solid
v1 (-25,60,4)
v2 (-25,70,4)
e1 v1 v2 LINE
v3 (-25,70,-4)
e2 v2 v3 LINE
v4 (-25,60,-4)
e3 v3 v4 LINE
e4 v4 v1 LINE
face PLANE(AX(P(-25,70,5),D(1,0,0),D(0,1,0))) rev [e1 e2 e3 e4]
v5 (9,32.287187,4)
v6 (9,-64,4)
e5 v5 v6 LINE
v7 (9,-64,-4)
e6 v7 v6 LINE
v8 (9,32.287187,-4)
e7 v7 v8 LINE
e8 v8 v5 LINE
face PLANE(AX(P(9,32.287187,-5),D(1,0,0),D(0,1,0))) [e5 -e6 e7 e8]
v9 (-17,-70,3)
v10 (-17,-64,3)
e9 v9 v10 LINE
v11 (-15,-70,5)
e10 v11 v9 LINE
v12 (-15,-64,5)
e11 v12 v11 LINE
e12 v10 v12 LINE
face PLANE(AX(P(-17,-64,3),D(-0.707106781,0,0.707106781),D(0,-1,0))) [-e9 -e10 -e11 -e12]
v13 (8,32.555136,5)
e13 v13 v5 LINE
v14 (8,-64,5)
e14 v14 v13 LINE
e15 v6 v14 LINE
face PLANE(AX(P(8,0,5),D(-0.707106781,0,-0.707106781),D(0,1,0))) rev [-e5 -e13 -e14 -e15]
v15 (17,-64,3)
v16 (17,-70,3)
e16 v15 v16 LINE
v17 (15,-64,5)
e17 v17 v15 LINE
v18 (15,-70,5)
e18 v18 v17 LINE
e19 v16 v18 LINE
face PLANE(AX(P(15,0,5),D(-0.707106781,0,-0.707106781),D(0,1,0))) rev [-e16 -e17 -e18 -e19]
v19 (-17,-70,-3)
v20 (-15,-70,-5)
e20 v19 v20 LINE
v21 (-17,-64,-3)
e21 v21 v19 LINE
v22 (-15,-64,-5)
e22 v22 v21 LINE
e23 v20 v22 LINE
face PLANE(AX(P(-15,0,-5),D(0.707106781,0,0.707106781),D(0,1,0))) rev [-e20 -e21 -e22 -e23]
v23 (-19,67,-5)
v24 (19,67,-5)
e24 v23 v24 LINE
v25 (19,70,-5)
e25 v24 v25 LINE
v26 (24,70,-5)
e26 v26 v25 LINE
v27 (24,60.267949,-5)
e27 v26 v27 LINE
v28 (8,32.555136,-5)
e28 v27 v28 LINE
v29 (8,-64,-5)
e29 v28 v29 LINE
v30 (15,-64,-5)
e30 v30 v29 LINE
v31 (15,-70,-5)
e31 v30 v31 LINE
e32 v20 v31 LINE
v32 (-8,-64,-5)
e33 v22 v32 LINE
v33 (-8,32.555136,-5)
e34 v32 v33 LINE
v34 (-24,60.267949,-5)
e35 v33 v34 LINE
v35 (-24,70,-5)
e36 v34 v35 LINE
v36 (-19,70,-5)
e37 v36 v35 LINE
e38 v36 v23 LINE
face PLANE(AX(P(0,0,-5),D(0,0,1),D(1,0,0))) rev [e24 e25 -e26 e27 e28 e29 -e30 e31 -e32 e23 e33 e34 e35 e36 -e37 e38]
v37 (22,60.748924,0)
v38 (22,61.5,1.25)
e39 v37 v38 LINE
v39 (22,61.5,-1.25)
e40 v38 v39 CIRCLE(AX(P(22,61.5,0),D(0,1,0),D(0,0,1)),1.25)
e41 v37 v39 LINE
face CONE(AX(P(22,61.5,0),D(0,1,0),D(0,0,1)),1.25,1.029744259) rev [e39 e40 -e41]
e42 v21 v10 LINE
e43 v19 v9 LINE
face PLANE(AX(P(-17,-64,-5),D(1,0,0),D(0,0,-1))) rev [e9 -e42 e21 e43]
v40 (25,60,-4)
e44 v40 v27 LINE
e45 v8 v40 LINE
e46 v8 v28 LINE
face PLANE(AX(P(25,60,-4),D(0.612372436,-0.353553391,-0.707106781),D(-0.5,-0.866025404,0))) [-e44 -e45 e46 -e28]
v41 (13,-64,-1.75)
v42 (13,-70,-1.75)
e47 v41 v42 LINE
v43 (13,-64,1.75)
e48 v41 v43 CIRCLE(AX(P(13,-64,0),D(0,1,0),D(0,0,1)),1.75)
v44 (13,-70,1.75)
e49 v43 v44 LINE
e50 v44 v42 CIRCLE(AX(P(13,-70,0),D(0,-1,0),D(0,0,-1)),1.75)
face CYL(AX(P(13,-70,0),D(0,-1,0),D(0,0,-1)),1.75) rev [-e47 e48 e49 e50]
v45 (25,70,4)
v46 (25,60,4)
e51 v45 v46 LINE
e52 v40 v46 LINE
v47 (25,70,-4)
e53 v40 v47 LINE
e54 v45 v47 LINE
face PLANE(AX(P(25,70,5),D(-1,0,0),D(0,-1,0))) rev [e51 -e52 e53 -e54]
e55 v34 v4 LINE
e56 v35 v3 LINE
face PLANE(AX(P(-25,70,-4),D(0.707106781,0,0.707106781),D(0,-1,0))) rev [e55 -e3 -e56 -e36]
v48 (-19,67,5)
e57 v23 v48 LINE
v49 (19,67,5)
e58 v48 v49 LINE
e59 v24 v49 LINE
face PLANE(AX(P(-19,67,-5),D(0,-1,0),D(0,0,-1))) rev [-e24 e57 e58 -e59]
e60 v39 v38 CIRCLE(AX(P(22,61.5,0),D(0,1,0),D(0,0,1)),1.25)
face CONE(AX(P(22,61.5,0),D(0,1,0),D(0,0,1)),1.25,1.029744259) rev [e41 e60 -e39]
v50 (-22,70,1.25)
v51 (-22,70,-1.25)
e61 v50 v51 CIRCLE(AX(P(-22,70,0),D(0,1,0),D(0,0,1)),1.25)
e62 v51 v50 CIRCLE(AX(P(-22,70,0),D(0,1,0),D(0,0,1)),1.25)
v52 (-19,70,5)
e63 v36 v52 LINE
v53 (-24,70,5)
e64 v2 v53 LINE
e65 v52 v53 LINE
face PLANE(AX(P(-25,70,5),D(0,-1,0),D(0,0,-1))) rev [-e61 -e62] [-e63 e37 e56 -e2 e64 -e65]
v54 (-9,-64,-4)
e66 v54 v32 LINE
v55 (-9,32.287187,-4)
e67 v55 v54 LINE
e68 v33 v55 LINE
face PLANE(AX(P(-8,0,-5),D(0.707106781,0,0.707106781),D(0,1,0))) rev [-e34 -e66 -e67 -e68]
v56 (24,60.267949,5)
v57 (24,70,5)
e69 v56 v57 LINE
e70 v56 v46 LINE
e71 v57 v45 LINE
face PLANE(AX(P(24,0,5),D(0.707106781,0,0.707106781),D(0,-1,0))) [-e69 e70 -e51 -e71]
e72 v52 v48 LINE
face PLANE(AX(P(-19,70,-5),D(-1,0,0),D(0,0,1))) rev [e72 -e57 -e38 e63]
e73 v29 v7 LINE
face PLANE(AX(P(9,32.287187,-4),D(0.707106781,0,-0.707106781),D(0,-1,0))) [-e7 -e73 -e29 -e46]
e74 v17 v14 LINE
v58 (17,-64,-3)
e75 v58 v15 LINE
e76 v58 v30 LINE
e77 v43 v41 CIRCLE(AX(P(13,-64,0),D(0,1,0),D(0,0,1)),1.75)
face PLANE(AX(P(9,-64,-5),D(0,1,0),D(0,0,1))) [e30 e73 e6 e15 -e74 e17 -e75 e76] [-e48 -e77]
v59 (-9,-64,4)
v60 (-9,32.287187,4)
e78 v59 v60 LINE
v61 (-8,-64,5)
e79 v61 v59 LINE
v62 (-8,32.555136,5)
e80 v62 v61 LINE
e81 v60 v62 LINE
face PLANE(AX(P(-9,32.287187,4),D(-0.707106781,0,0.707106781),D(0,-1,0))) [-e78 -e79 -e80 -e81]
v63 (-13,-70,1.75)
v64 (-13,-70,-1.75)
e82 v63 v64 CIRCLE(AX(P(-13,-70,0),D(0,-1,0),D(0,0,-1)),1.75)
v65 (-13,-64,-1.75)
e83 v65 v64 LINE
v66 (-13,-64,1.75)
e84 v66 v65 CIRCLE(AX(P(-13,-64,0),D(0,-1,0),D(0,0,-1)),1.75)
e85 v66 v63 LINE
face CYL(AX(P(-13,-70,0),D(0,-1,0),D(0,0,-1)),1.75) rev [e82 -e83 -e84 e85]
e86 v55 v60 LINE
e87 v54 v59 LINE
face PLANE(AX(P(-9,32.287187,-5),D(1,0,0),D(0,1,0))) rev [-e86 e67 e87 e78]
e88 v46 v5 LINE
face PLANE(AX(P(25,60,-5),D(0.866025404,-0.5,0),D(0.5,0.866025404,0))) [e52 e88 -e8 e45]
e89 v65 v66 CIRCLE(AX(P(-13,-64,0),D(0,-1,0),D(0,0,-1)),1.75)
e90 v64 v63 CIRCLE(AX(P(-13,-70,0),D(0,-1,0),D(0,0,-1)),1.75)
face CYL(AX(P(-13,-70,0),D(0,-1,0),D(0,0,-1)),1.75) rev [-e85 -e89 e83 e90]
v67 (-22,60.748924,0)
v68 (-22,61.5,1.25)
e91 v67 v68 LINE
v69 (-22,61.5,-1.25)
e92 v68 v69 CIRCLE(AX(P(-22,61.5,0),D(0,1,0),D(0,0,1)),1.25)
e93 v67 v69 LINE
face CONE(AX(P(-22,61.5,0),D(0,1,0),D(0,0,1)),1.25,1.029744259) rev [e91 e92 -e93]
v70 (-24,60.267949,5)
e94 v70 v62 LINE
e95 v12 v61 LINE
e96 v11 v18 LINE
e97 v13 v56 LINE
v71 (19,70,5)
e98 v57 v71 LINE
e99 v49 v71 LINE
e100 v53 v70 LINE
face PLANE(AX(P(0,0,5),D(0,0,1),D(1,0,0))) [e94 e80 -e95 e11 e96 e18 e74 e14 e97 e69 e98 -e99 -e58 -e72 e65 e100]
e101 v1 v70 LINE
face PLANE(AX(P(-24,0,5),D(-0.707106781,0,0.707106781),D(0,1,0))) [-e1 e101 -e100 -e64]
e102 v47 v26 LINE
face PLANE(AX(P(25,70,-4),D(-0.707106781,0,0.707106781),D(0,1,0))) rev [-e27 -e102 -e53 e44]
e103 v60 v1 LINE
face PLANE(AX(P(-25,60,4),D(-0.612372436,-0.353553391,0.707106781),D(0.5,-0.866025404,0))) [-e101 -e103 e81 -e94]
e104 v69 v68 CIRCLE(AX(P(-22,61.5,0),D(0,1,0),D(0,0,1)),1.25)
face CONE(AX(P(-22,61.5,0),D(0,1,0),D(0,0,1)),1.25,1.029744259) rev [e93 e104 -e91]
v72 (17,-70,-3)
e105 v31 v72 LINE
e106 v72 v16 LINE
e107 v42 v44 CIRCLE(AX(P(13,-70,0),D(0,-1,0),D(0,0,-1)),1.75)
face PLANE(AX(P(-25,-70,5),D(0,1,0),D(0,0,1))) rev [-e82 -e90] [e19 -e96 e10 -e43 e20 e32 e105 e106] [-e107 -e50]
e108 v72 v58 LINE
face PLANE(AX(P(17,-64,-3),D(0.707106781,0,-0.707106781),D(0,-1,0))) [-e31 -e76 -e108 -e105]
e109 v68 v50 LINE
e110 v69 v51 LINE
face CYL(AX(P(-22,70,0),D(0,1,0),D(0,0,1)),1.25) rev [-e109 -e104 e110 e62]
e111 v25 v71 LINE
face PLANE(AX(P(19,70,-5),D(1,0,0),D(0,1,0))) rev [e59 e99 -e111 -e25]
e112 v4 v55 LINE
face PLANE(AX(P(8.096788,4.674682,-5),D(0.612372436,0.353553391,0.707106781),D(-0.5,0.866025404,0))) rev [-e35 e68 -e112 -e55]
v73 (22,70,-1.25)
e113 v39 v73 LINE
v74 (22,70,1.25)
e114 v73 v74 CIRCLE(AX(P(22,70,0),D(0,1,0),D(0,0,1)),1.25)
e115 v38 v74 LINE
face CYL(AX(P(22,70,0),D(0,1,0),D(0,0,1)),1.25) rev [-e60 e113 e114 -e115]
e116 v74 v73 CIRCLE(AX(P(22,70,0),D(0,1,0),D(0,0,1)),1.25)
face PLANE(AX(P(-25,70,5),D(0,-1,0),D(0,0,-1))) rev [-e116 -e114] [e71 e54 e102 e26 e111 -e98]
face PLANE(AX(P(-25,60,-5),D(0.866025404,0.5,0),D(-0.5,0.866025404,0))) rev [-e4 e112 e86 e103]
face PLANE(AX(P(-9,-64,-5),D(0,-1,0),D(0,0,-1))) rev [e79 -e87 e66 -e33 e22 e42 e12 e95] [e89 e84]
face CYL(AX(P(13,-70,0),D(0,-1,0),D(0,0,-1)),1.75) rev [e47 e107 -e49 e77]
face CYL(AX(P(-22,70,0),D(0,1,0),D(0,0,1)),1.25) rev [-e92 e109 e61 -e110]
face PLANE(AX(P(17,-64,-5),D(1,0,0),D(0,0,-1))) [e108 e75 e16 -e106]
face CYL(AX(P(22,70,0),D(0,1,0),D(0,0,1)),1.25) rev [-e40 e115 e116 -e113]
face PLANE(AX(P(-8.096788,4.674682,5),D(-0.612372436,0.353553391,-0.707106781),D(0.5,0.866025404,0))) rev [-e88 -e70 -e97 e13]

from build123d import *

# Parameters (mm, degrees)
SKETCH1_W                      = 50
SKETCH1_H                      = 140
BOSS_EXTRUDE1_DEPTH            = 5
CUT_EXTRUDE1_DEPTH             = 76
SKETCH3_W                      = 38
SKETCH3_H                      = 3
CUT_EXTRUDE2_DEPTH             = 76
M3_TAPPED_HOLE1_D              = 2.5
M3_TAPPED_HOLE1_DEPTH          = 8.5
M3_TAPPED_HOLE1_TIP            = 0.751075774
F_3_5_3_5_DIAMETER_HOLE1_D     = 3.5
F_3_5_3_5_DIAMETER_HOLE1_DEPTH = 6
CHAMFER1_SIZE                  = 2
CHAMFER2_SIZE                  = 1


with BuildPart() as part:
    # Sketch1 → Boss-Extrude1 (new, symmetric)
    with BuildSketch(Plane.XY):
        Rectangle(SKETCH1_W, SKETCH1_H)
    extrude(amount=BOSS_EXTRUDE1_DEPTH, both=True)

    # Sketch2 → Cut-Extrude1 (cut, through all)
    with BuildSketch(Plane.XY.offset(5)):
        Polygon((-25, 60), (-9, 32.287187079), (-9, -64), (-17, -64), (-17, -70), (-25, -70), align=None)
    cut_extrude1 = extrude(amount=-CUT_EXTRUDE1_DEPTH, mode=Mode.SUBTRACT)

    # Mirror1: Cut-Extrude1 across plane
    add(cut_extrude1.mirror(Plane(origin=(0, 0, 0), x_dir=(0, 0, 1), z_dir=(1, 0, 0))), mode=Mode.SUBTRACT)

    # Sketch3 → Cut-Extrude2 (cut, through all)
    with BuildSketch(Plane.XY.offset(5)):
        with Locations((0, 68.5)):
            Rectangle(SKETCH3_W, SKETCH3_H)
    extrude(amount=-CUT_EXTRUDE2_DEPTH, mode=Mode.SUBTRACT)

    # M3 Tapped Hole1
    with Locations(Plane(origin=(0, 70, 0), x_dir=(1, 0, 0), z_dir=(0, 1, 0))):
        with Locations((-22, 0), (22, 0)):
            Hole(M3_TAPPED_HOLE1_D / 2, depth=M3_TAPPED_HOLE1_DEPTH)
            with Locations((0, 0, -(M3_TAPPED_HOLE1_DEPTH + M3_TAPPED_HOLE1_TIP / 2))):  # 118° drill point
                Cone(0, M3_TAPPED_HOLE1_D / 2, M3_TAPPED_HOLE1_TIP, mode=Mode.SUBTRACT)

    # Ø3.5 (3.5) Diameter Hole1
    with Locations(Plane(origin=(0, -70, 0), x_dir=(-1, 0, 0), z_dir=(0, -1, 0))):
        with Locations((13, 0), (-13, 0)):
            Hole(F_3_5_3_5_DIAMETER_HOLE1_D / 2, depth=F_3_5_3_5_DIAMETER_HOLE1_DEPTH)

    # Chamfer1
    chamfer1_edges = [part.edges().sort_by_distance(p)[0] for p in [
        (-17, -67, -5),
        (-17, -67, 5),
        (17, -67, 5),
        (17, -67, -5),
    ]]
    chamfer(chamfer1_edges, length=CHAMFER1_SIZE)

    # Chamfer2
    chamfer2_edges = [part.edges().sort_by_distance(p)[0] for p in [
        (-25, 65, 5),
        (-17, 46.143593539, -5),
        (-9, -15.856406461, -5),
        (-9, -15.856406461, 5),
        (-17, 46.143593539, 5),
        (25, 65, -5),
        (25, 65, 5),
        (9, -15.856406461, 5),
        (17, 46.143593539, 5),
        (9, -15.856406461, -5),
        (17, 46.143593539, -5),
        (-25, 65, -5),
    ]]
    chamfer(chamfer2_edges, length=CHAMFER2_SIZE)


solid = part.part
